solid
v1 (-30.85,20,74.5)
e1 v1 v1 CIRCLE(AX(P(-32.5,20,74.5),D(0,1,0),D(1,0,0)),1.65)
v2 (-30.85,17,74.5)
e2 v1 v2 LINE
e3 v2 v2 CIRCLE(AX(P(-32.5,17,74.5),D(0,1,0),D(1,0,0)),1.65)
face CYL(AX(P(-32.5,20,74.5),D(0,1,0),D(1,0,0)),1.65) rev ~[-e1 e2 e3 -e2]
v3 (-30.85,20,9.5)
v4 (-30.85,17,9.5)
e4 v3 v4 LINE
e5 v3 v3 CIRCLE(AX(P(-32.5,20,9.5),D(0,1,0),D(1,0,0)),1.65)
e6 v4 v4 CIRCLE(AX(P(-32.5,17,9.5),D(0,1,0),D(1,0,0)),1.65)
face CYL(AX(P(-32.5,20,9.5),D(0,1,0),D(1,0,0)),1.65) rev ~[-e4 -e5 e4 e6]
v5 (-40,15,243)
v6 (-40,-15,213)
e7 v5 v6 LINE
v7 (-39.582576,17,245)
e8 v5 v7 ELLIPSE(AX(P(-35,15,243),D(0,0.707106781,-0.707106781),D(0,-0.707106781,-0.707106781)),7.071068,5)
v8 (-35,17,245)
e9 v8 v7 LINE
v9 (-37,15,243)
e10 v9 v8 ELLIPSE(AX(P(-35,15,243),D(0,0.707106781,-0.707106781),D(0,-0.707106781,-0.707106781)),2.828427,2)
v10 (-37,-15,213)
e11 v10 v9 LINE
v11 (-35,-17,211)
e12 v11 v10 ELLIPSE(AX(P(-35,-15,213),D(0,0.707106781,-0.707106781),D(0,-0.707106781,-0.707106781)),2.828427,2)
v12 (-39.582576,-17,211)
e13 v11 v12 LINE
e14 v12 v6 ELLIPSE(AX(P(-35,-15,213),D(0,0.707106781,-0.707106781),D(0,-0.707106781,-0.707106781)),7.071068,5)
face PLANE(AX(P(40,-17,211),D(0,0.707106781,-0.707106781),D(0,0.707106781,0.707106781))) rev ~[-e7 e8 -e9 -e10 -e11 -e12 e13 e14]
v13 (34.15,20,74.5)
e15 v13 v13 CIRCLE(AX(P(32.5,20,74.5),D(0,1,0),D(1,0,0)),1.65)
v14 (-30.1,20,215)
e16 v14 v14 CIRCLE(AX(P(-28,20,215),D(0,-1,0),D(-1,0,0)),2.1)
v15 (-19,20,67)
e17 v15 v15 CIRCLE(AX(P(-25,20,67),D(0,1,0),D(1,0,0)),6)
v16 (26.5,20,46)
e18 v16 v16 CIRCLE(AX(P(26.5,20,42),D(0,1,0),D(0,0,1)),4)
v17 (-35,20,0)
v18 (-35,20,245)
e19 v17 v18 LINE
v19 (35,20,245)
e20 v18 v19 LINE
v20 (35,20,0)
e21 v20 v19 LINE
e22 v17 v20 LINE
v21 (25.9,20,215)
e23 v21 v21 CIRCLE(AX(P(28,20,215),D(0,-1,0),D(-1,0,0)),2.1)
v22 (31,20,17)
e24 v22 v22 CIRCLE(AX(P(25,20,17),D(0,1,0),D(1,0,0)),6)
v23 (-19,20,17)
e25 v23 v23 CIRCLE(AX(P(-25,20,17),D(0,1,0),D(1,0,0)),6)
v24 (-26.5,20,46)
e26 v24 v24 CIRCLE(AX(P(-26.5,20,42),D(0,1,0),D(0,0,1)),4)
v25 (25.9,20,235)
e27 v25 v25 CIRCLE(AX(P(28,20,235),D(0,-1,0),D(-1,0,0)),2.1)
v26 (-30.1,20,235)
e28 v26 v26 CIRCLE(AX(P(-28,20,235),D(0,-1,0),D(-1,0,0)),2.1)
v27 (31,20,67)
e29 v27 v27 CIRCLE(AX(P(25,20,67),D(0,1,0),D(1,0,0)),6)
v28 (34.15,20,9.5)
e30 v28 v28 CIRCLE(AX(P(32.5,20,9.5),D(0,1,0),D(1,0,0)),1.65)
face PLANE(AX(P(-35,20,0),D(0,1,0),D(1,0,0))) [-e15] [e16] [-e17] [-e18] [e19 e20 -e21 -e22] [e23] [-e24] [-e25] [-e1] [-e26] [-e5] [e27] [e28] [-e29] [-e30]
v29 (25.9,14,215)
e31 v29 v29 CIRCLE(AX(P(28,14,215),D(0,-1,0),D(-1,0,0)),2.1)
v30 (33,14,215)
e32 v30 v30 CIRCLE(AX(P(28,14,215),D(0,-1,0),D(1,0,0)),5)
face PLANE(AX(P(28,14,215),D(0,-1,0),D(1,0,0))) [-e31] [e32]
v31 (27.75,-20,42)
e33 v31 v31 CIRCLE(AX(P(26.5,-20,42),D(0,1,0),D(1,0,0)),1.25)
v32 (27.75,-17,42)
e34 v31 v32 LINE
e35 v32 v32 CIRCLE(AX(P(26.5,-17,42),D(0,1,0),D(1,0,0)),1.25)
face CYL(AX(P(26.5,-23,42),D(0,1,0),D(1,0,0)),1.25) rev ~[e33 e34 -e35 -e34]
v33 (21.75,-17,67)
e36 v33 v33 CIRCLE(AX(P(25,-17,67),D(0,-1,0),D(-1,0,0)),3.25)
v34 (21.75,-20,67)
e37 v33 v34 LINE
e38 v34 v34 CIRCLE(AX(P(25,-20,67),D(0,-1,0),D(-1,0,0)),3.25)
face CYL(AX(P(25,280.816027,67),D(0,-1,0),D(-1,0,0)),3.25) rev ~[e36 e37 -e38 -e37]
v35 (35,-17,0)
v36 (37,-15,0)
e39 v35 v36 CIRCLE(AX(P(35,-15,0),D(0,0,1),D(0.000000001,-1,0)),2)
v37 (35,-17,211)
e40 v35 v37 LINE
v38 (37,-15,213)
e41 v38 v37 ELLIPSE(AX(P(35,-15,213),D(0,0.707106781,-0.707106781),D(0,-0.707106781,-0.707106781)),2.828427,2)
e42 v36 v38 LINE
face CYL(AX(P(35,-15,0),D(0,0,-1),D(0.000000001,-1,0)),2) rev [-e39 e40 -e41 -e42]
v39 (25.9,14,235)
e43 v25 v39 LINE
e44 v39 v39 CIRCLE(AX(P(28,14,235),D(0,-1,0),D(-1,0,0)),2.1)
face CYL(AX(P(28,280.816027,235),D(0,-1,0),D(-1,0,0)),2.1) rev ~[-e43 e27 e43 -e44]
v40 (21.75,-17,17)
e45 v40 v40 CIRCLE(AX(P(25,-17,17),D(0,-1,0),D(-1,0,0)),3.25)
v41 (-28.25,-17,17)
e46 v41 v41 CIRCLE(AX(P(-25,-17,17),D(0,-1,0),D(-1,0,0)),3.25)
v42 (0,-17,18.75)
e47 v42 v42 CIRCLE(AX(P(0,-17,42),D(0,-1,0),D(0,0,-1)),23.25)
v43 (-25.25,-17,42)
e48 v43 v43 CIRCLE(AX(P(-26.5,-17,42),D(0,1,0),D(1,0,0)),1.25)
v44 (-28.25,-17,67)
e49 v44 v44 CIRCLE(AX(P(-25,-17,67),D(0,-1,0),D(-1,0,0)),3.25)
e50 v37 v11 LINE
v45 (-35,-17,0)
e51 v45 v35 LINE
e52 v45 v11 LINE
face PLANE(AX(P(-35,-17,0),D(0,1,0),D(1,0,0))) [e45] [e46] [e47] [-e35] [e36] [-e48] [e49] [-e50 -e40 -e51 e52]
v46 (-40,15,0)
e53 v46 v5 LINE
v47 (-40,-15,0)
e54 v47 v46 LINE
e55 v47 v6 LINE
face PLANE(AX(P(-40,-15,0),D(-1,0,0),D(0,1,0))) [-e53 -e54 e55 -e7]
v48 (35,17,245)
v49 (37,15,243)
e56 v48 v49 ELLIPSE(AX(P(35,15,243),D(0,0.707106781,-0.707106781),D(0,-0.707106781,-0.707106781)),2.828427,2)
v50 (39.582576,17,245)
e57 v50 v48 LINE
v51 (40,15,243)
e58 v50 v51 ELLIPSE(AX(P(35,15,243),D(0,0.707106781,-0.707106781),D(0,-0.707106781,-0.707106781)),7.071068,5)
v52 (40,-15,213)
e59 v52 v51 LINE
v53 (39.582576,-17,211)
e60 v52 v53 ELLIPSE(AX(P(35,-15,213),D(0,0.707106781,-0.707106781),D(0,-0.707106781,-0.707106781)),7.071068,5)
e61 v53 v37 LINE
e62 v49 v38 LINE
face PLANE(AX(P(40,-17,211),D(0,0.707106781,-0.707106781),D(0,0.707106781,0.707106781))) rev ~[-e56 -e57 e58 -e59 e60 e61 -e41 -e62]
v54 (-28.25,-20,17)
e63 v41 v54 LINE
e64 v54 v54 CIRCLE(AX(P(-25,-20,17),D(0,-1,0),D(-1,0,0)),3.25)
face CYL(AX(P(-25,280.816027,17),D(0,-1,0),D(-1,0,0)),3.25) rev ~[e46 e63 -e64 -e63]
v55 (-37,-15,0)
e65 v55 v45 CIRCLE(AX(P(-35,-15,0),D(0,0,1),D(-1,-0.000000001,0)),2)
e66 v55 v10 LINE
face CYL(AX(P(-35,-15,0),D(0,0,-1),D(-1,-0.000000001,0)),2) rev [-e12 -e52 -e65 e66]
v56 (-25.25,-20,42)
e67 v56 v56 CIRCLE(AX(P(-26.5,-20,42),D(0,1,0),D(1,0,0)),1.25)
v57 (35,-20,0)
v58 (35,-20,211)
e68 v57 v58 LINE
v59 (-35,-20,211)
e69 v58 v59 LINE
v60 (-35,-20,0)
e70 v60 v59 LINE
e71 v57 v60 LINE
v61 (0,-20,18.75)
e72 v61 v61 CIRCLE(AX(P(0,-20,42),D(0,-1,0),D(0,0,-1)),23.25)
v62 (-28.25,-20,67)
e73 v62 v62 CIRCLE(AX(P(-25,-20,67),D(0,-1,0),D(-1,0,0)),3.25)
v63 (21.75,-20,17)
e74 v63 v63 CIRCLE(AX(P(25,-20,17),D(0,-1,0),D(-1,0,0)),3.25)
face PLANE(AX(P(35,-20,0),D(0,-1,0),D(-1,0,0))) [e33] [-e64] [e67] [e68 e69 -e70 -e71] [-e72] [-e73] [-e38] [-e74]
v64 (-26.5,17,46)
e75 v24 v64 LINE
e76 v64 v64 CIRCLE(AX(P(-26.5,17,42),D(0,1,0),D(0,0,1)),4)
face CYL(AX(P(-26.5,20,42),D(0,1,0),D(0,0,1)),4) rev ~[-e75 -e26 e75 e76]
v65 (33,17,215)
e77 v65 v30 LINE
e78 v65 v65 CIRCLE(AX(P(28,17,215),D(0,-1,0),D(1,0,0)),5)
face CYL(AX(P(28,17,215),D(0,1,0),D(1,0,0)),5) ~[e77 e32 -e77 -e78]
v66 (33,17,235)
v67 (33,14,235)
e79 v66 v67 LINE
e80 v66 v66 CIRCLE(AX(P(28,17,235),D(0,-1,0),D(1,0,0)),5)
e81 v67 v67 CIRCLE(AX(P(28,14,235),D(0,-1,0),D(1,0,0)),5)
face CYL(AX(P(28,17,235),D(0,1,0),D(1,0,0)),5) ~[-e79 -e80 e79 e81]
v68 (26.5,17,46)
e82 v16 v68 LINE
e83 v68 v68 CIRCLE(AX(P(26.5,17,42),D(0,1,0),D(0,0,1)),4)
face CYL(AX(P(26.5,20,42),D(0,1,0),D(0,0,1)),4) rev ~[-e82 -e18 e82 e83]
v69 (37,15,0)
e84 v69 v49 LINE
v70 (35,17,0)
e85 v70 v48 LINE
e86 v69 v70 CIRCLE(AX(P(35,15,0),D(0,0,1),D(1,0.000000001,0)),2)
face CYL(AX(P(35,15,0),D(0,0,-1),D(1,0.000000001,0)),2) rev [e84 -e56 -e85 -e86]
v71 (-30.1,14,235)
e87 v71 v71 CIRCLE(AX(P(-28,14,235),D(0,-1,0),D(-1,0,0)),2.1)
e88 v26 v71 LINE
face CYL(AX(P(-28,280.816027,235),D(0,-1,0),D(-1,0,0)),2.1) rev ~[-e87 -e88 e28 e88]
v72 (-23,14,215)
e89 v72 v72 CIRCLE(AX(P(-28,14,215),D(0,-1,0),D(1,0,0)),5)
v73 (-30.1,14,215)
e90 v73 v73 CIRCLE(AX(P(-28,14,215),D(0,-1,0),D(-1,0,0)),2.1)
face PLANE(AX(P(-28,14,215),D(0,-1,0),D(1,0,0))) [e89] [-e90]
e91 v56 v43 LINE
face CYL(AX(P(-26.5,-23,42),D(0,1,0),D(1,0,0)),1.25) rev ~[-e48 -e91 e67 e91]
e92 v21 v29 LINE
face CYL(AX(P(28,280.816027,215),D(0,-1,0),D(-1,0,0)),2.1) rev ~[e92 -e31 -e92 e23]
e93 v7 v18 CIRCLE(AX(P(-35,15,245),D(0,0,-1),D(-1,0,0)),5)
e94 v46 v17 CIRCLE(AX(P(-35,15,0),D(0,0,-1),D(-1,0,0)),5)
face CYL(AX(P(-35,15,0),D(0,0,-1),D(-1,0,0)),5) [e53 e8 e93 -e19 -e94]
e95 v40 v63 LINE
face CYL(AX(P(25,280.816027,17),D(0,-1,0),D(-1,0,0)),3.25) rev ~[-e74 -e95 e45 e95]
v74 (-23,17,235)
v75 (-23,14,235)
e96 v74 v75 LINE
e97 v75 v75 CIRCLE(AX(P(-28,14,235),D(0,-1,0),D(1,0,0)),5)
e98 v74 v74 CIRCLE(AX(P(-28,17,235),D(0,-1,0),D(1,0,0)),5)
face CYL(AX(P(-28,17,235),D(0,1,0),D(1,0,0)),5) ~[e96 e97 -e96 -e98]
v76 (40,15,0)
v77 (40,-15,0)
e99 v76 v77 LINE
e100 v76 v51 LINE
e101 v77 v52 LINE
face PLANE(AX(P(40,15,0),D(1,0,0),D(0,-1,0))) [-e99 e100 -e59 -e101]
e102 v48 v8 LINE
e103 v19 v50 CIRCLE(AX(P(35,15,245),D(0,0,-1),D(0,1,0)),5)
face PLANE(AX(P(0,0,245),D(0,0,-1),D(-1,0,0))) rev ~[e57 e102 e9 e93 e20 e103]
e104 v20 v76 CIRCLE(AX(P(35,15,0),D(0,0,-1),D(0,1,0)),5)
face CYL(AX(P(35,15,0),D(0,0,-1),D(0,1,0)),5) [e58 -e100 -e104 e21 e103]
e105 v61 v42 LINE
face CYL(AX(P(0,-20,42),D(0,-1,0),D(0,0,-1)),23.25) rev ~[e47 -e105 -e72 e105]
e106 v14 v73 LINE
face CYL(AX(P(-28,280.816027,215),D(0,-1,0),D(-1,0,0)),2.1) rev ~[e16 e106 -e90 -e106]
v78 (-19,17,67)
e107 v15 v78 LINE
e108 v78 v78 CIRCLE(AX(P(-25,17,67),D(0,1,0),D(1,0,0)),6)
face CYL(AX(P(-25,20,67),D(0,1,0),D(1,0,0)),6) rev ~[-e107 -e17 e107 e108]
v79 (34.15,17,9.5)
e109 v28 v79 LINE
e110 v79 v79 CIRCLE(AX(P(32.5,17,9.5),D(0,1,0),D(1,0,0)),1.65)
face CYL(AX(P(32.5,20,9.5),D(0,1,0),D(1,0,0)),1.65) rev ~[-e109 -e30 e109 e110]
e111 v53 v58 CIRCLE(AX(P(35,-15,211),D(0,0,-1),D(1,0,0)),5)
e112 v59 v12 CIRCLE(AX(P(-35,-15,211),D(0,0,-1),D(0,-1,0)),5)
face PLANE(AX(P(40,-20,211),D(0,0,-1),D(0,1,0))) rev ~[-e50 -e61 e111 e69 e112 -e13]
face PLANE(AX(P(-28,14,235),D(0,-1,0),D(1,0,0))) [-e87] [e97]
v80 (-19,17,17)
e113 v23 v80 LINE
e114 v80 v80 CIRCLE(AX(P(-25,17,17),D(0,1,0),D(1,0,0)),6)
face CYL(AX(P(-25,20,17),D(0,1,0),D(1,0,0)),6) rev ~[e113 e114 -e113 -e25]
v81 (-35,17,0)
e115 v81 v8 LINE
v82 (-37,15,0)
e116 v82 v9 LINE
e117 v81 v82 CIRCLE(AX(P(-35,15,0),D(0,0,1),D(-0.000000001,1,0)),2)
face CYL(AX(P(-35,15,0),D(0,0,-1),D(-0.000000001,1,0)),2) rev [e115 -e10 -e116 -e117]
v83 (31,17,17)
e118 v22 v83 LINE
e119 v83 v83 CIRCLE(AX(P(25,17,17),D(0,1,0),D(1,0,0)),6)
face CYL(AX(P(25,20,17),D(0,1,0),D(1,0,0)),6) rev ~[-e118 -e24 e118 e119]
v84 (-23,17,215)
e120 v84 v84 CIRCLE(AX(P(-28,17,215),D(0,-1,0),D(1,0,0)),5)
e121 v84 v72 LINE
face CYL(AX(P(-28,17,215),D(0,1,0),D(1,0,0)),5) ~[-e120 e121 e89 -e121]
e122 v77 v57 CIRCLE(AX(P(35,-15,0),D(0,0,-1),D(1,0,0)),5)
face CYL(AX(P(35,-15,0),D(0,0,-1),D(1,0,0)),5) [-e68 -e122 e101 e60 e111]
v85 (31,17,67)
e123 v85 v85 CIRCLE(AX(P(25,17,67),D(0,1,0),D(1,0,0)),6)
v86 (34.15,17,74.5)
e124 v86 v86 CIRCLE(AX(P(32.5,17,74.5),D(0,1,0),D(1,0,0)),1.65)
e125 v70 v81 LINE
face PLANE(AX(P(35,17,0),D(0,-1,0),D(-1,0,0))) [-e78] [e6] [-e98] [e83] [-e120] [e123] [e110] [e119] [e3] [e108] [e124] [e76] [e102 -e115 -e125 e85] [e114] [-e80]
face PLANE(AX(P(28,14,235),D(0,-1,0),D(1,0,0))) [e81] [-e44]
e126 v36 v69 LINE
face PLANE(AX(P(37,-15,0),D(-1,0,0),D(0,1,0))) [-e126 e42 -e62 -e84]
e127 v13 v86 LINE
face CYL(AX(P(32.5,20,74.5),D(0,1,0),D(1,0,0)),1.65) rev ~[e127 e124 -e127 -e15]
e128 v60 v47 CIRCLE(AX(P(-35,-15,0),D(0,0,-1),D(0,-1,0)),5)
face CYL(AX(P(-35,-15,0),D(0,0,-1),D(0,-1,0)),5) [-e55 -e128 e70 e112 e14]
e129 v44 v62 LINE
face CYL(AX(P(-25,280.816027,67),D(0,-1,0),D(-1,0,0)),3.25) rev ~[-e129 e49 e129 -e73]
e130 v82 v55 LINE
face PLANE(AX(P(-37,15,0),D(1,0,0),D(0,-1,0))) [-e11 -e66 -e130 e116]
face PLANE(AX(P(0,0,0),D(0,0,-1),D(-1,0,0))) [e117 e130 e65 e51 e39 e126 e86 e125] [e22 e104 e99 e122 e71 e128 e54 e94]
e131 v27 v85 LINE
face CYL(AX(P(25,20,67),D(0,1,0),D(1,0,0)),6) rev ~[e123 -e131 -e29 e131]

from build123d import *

# Parameters (mm, degrees)
BOSS_EXTRUDE1_DEPTH             = 245
SKETCH6_R                       = 23.25
CUT_EXTRUDE1_DEPTH              = 3
F_6_5_6_5_DIAMETER_HOLE1_D      = 6.5
F_12_0_12_DIAMETER_HOLE1_REACH  = 253.446
F_12_0_12_DIAMETER_HOLE1_BORE_R = 6
M4_TAPPED_HOLE1_REACH           = 253.446
M4_TAPPED_HOLE1_BORE_R          = 1.65
CUT_EXTRUDE2_DEPTH              = 259.505319094
SKETCH12_R                      = 5
BOSS_EXTRUDE2_DEPTH             = 3
M5_TAPPED_HOLE1_D               = 4.2
M3_TAPPED_HOLE1_D               = 2.5
M3_TAPPED_HOLE1_DEPTH           = 3
CUT_EXTRUDE3_REACH              = 253.446
SKETCH17_R                      = 4


with BuildPart() as part:
    # Sketch1 → Boss-Extrude1 (new body)
    with BuildSketch(Plane.XY):
        with BuildLine():
            Line((-35, 20), (35, 20))
            ThreePointArc((35, 20), (38.535533906, 18.535533906), (40, 15))
            Line((40, 15), (40, -15))
            ThreePointArc((40, -15), (38.535533906, -18.535533906), (35, -20))
            Line((35, -20), (-35, -20))
            ThreePointArc((-35, -20), (-38.535533906, -18.535533906), (-40, -15))
            Line((-40, -15), (-40, 15))
            ThreePointArc((-40, 15), (-38.535533906, 18.535533906), (-35, 20))
        make_face()
        with BuildLine():
            Line((-37, 15), (-37, -15))
            ThreePointArc((-37, -15), (-36.414213562, -16.414213562), (-35, -17))
            Line((-35, -17), (35, -17))
            ThreePointArc((35, -17), (36.414213562, -16.414213562), (37, -15))
            Line((37, -15), (37, 15))
            ThreePointArc((37, 15), (36.414213562, 16.414213562), (35, 17))
            Line((35, 17), (-35, 17))
            ThreePointArc((-35, 17), (-36.414213562, 16.414213562), (-37, 15))
        make_face(mode=Mode.SUBTRACT)
    extrude(amount=BOSS_EXTRUDE1_DEPTH)

    # Sketch6 → Cut-Extrude1 (cut)
    with BuildSketch(Plane.XZ.offset(20)):
        with Locations(Location((0, 42, 0), (0, 0, 270))):
            Circle(SKETCH6_R)
    extrude(amount=-CUT_EXTRUDE1_DEPTH, mode=Mode.SUBTRACT)

    # Ø6.5 (6.5) Diameter Hole1 (through all)
    with Locations(Plane(origin=(0, 20, 0), x_dir=(1, 0, 0), z_dir=(0, 1, 0))):
        with Locations((-25, -17), (25, -17), (25, -67), (-25, -67)):
            Hole(F_6_5_6_5_DIAMETER_HOLE1_D / 2)

    # Ø12.0 (12) Diameter Hole1 bore → Ø12.0 (12) Diameter Hole1 (cut, up to next)
    with BuildSketch(Plane(origin=(0, 20, 0), x_dir=(1, 0, 0), z_dir=(0, 1, 0)), mode=Mode.PRIVATE) as f_12_0_12_diameter_hole1_sk1:
        with Locations((-25, -17)):
            Circle(F_12_0_12_DIAMETER_HOLE1_BORE_R)
    f_12_0_12_diameter_hole1_tool1 = extrude(f_12_0_12_diameter_hole1_sk1.sketch, amount=-F_12_0_12_DIAMETER_HOLE1_REACH, mode=Mode.PRIVATE) & part.part
    # Ø12.0 (12) Diameter Hole1 bore → Ø12.0 (12) Diameter Hole1 (cut, up to next)
    with BuildSketch(Plane(origin=(0, 20, 0), x_dir=(1, 0, 0), z_dir=(0, 1, 0)), mode=Mode.PRIVATE) as f_12_0_12_diameter_hole1_sk2:
        with Locations((25, -17)):
            Circle(F_12_0_12_DIAMETER_HOLE1_BORE_R)
    f_12_0_12_diameter_hole1_tool2 = extrude(f_12_0_12_diameter_hole1_sk2.sketch, amount=-F_12_0_12_DIAMETER_HOLE1_REACH, mode=Mode.PRIVATE) & part.part
    # Ø12.0 (12) Diameter Hole1 bore → Ø12.0 (12) Diameter Hole1 (cut, up to next)
    with BuildSketch(Plane(origin=(0, 20, 0), x_dir=(1, 0, 0), z_dir=(0, 1, 0)), mode=Mode.PRIVATE) as f_12_0_12_diameter_hole1_sk3:
        with Locations((25, -67)):
            Circle(F_12_0_12_DIAMETER_HOLE1_BORE_R)
    f_12_0_12_diameter_hole1_tool3 = extrude(f_12_0_12_diameter_hole1_sk3.sketch, amount=-F_12_0_12_DIAMETER_HOLE1_REACH, mode=Mode.PRIVATE) & part.part
    # Ø12.0 (12) Diameter Hole1 bore → Ø12.0 (12) Diameter Hole1 (cut, up to next)
    with BuildSketch(Plane(origin=(0, 20, 0), x_dir=(1, 0, 0), z_dir=(0, 1, 0)), mode=Mode.PRIVATE) as f_12_0_12_diameter_hole1_sk4:
        with Locations((-25, -67)):
            Circle(F_12_0_12_DIAMETER_HOLE1_BORE_R)
    f_12_0_12_diameter_hole1_tool4 = extrude(f_12_0_12_diameter_hole1_sk4.sketch, amount=-F_12_0_12_DIAMETER_HOLE1_REACH, mode=Mode.PRIVATE) & part.part
    add(f_12_0_12_diameter_hole1_tool1.solids().sort_by_distance((-25, 20, 17))[0], mode=Mode.SUBTRACT)
    add(f_12_0_12_diameter_hole1_tool2.solids().sort_by_distance((25, 20, 17))[0], mode=Mode.SUBTRACT)
    add(f_12_0_12_diameter_hole1_tool3.solids().sort_by_distance((25, 20, 67))[0], mode=Mode.SUBTRACT)
    add(f_12_0_12_diameter_hole1_tool4.solids().sort_by_distance((-25, 20, 67))[0], mode=Mode.SUBTRACT)

    # M4 Tapped Hole1 bore → M4 Tapped Hole1 (cut, up to next)
    with BuildSketch(Plane(origin=(0, 20, 0), x_dir=(1, 0, 0), z_dir=(0, 1, 0)), mode=Mode.PRIVATE) as m4_tapped_hole1_sk1:
        with Locations((-32.5, -9.5)):
            Circle(M4_TAPPED_HOLE1_BORE_R)
    m4_tapped_hole1_tool1 = extrude(m4_tapped_hole1_sk1.sketch, amount=-M4_TAPPED_HOLE1_REACH, mode=Mode.PRIVATE) & part.part
    # M4 Tapped Hole1 bore → M4 Tapped Hole1 (cut, up to next)
    with BuildSketch(Plane(origin=(0, 20, 0), x_dir=(1, 0, 0), z_dir=(0, 1, 0)), mode=Mode.PRIVATE) as m4_tapped_hole1_sk2:
        with Locations((32.5, -9.5)):
            Circle(M4_TAPPED_HOLE1_BORE_R)
    m4_tapped_hole1_tool2 = extrude(m4_tapped_hole1_sk2.sketch, amount=-M4_TAPPED_HOLE1_REACH, mode=Mode.PRIVATE) & part.part
    # M4 Tapped Hole1 bore → M4 Tapped Hole1 (cut, up to next)
    with BuildSketch(Plane(origin=(0, 20, 0), x_dir=(1, 0, 0), z_dir=(0, 1, 0)), mode=Mode.PRIVATE) as m4_tapped_hole1_sk3:
        with Locations((32.5, -74.5)):
            Circle(M4_TAPPED_HOLE1_BORE_R)
    m4_tapped_hole1_tool3 = extrude(m4_tapped_hole1_sk3.sketch, amount=-M4_TAPPED_HOLE1_REACH, mode=Mode.PRIVATE) & part.part
    # M4 Tapped Hole1 bore → M4 Tapped Hole1 (cut, up to next)
    with BuildSketch(Plane(origin=(0, 20, 0), x_dir=(1, 0, 0), z_dir=(0, 1, 0)), mode=Mode.PRIVATE) as m4_tapped_hole1_sk4:
        with Locations((-32.5, -74.5)):
            Circle(M4_TAPPED_HOLE1_BORE_R)
    m4_tapped_hole1_tool4 = extrude(m4_tapped_hole1_sk4.sketch, amount=-M4_TAPPED_HOLE1_REACH, mode=Mode.PRIVATE) & part.part
    add(m4_tapped_hole1_tool1.solids().sort_by_distance((-32.5, 20, 9.5))[0], mode=Mode.SUBTRACT)
    add(m4_tapped_hole1_tool2.solids().sort_by_distance((32.5, 20, 9.5))[0], mode=Mode.SUBTRACT)
    add(m4_tapped_hole1_tool3.solids().sort_by_distance((32.5, 20, 74.5))[0], mode=Mode.SUBTRACT)
    add(m4_tapped_hole1_tool4.solids().sort_by_distance((-32.5, 20, 74.5))[0], mode=Mode.SUBTRACT)

    # Sketch9 → Cut-Extrude2 (cut, through all)
    with BuildSketch(Plane(origin=(40, 0, 0), x_dir=(0, 0, -1), z_dir=(1, 0, 0))):
        Polygon((-245, 17), (-245, -20), (-211, -20), (-211, -17), align=None)
    extrude(amount=-CUT_EXTRUDE2_DEPTH, mode=Mode.SUBTRACT)

    # Sketch12 → Boss-Extrude2 (add)
    with BuildSketch(Plane.XZ.offset(-17)):
        with Locations((-28, 215)):
            Circle(SKETCH12_R)
        with Locations((-28, 235)):
            Circle(SKETCH12_R)
        with Locations((28, 215)):
            Circle(SKETCH12_R)
        with Locations((28, 235)):
            Circle(SKETCH12_R)
    extrude(amount=BOSS_EXTRUDE2_DEPTH)

    # M5 Tapped Hole1 (through all)
    with Locations(Plane(origin=(-35, 20, 20), x_dir=(1, 0, 0), z_dir=(0, 1, 0))):
        with Locations((7, -195), (7, -215), (63, -195), (63, -215)):
            Hole(M5_TAPPED_HOLE1_D / 2)

    # M3 Tapped Hole1
    with Locations(Plane(origin=(0, -20, 0), x_dir=(-1, 0, 0), z_dir=(0, -1, 0))):
        with Locations((26.5, -42), (-26.5, -42)):
            Hole(M3_TAPPED_HOLE1_D / 2, depth=M3_TAPPED_HOLE1_DEPTH)

    # Sketch17 → Cut-Extrude3 (cut, up to next)
    with BuildSketch(Plane(origin=(0, 20, 0), x_dir=(1, 0, 0), z_dir=(0, 1, 0)), mode=Mode.PRIVATE) as cut_extrude3_sk1:
        with Locations(Location((-26.5, -42, 0), (0, 0, 270))):
            Circle(SKETCH17_R)
    cut_extrude3_tool1 = extrude(cut_extrude3_sk1.sketch, amount=-CUT_EXTRUDE3_REACH, mode=Mode.PRIVATE) & part.part
    # Sketch17 → Cut-Extrude3 (cut, up to next)
    with BuildSketch(Plane(origin=(0, 20, 0), x_dir=(1, 0, 0), z_dir=(0, 1, 0)), mode=Mode.PRIVATE) as cut_extrude3_sk2:
        with Locations(Location((26.5, -42, 0), (0, 0, 270))):
            Circle(SKETCH17_R)
    cut_extrude3_tool2 = extrude(cut_extrude3_sk2.sketch, amount=-CUT_EXTRUDE3_REACH, mode=Mode.PRIVATE) & part.part
    add(cut_extrude3_tool1.solids().sort_by_distance((-26.5, 20, 42))[0], mode=Mode.SUBTRACT)
    add(cut_extrude3_tool2.solids().sort_by_distance((26.5, 20, 42))[0], mode=Mode.SUBTRACT)


solid = part.part
